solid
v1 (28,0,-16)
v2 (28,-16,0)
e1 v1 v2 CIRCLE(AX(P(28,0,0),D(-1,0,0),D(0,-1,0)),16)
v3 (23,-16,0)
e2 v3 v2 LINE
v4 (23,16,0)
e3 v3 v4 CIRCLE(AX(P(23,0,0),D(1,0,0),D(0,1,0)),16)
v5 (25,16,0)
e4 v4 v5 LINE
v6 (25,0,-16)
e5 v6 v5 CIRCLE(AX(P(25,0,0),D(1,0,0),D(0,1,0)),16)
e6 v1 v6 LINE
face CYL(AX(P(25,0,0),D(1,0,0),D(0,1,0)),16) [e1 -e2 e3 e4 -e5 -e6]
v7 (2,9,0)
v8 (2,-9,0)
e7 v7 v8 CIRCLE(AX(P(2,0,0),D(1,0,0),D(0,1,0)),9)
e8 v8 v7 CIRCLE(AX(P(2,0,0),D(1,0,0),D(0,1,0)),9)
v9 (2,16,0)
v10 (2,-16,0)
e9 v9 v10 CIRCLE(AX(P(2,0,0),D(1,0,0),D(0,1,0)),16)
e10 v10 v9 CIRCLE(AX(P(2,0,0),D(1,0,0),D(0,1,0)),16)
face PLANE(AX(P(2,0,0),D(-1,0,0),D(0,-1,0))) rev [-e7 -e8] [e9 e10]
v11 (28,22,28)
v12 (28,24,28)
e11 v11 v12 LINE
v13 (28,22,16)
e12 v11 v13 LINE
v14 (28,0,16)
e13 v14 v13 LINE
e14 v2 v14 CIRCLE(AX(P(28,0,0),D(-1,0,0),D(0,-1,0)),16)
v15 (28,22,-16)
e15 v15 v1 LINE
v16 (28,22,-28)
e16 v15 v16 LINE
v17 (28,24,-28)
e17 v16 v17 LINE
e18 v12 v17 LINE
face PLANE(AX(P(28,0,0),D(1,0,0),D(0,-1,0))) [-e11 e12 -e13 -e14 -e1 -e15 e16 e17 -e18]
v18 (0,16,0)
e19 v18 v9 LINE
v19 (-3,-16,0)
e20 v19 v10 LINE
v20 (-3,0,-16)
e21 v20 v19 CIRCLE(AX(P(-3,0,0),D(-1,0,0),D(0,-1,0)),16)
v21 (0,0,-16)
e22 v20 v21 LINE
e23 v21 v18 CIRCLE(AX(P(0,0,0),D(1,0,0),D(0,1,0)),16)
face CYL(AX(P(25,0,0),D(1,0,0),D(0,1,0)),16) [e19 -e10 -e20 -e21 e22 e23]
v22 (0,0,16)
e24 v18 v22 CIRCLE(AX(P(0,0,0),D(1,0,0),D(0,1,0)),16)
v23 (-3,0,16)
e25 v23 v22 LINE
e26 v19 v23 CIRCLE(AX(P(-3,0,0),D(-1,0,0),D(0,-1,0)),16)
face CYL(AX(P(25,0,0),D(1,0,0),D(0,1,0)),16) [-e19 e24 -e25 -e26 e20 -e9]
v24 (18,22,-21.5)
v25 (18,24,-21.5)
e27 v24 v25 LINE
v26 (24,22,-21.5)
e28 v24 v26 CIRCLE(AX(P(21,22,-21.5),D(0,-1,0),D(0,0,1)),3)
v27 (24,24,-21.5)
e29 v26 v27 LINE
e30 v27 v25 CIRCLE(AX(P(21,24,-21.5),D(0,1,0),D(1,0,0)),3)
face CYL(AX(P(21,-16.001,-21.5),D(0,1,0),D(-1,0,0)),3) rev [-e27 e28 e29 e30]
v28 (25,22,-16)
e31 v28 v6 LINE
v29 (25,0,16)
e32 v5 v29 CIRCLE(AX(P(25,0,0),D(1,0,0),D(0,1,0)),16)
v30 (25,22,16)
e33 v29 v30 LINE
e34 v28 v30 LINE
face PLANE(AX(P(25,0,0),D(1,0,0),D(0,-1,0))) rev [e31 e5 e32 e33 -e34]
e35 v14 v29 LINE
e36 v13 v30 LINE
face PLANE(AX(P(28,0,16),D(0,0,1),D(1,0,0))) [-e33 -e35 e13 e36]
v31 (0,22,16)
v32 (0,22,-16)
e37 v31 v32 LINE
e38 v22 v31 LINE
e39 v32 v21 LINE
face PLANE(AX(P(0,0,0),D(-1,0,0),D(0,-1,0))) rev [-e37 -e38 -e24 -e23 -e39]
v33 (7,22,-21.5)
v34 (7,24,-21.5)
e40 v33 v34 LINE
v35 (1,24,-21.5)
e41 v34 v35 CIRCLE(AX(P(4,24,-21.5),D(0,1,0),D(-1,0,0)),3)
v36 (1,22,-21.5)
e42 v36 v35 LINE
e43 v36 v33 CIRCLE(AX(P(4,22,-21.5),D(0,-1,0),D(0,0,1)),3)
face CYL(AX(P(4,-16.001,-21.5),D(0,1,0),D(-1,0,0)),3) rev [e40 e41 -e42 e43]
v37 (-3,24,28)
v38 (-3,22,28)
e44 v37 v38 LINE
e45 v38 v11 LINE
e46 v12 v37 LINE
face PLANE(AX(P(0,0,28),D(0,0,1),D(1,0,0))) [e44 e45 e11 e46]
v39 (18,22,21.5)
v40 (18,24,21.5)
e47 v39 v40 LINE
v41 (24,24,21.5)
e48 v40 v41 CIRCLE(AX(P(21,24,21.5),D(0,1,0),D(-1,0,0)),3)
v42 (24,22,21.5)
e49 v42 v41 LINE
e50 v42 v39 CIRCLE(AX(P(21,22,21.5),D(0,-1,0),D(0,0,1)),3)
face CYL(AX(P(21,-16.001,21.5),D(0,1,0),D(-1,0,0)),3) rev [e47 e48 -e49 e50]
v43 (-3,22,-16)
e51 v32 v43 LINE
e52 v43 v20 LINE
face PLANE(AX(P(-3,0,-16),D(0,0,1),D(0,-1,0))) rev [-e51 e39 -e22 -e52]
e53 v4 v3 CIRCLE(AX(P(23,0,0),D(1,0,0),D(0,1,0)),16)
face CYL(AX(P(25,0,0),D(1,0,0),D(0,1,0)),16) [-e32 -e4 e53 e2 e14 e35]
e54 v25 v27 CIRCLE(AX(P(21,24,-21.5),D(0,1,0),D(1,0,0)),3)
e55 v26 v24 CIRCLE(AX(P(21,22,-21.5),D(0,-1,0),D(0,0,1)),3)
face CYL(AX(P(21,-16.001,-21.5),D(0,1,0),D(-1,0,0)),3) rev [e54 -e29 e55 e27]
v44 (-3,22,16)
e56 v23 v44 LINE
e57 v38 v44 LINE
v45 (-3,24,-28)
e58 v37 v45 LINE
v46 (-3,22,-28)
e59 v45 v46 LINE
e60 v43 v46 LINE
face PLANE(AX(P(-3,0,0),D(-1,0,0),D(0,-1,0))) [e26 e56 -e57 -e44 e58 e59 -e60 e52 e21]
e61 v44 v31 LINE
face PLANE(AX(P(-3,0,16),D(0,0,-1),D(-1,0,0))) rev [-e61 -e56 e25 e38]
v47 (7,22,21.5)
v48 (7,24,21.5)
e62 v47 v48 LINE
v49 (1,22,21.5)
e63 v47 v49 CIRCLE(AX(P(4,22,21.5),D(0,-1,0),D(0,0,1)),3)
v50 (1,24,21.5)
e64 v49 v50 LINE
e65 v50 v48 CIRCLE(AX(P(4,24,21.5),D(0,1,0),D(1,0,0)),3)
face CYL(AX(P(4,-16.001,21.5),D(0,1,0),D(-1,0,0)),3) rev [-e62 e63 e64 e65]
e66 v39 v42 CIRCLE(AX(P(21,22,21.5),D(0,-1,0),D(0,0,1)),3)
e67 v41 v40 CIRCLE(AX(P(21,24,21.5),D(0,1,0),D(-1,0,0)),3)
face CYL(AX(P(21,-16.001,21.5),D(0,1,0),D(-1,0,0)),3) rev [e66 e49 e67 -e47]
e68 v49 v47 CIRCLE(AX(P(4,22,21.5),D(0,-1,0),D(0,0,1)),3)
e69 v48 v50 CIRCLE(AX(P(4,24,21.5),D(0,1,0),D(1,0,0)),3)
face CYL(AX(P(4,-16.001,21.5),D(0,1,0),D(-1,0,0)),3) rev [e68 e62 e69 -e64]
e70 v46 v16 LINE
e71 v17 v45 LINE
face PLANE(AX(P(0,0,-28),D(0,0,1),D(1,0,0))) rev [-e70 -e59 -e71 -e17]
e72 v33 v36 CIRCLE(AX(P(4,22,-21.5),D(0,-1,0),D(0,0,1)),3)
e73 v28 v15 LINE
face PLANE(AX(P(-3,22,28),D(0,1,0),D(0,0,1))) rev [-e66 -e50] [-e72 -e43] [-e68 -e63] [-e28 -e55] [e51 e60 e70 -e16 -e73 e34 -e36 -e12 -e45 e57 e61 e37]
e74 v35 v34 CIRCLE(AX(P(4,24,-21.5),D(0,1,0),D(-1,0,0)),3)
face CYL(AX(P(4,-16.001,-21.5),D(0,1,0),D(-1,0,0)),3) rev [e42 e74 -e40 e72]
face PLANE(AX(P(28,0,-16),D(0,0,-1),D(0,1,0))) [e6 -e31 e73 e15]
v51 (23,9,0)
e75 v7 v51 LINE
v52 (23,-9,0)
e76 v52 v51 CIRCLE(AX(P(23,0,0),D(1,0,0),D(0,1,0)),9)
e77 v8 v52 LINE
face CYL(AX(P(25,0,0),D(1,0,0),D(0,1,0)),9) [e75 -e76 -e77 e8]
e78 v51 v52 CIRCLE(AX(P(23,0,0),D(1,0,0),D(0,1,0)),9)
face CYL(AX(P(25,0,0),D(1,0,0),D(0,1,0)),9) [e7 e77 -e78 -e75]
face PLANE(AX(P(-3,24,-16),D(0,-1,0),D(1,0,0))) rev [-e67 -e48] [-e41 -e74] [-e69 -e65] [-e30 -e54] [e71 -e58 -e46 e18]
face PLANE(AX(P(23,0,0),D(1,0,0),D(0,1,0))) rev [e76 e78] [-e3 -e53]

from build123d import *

# Parameters (mm, degrees)
EXTRUDE_START       = 3
EXTRUDE_1_DEPTH     = 3
SKETCH_4_W          = 31
SKETCH_4_H          = 2
EXTRUDE_2_DEPTH     = 28
CUT_EXTRUDE_1_REACH = 58.285
SKETCH_5_R          = 3


with BuildPart() as part:
    # 草图1 → 旋转1 (revolve)
    with BuildSketch(Plane.XY):
        Polygon((2, 16), (0, 16), (0, 0), (25, 0), (25, 16), (23, 16), (23, 9), (2, 9), align=None)
    revolve(axis=Axis((25, 0, 0), (-1, 0, 0)))

    # 草图2 → 凸台-拉伸1 (add)
    with BuildSketch(Plane.ZY.offset(EXTRUDE_START)):
        with BuildLine():
            Line((-16, 0), (-16, 24))
            Line((-16, 24), (16, 24))
            Line((16, 24), (16, 0))
            ThreePointArc((16, 0), (0, -16), (-16, 0))
        make_face()
    extrude_1 = extrude(amount=-EXTRUDE_1_DEPTH)

    # 镜向1: 凸台-拉伸1 across plane
    add(extrude_1.mirror(Plane(origin=(12.5, 0, 0), x_dir=(0, 0, 1), z_dir=(1, 0, 0))))

    # 草图4 → 凸台-拉伸2 (add, symmetric)
    with BuildSketch(Plane.XY):
        with Locations((12.5, 23)):
            Rectangle(SKETCH_4_W, SKETCH_4_H)
    extrude(amount=EXTRUDE_2_DEPTH, both=True)

    # 草图5 → 切除-拉伸1 (cut, up to next)
    with BuildSketch(Plane(origin=(0, 24, 0), x_dir=(1, 0, 0), z_dir=(0, 1, 0)), mode=Mode.PRIVATE) as cut_extrude_1_sk1:
        with Locations(Location((4, 21.5, 0), (0, 0, 180))):
            Circle(SKETCH_5_R)
    cut_extrude_1_tool1 = extrude(cut_extrude_1_sk1.sketch, amount=-CUT_EXTRUDE_1_REACH, mode=Mode.PRIVATE) & part.part
    # 草图5 → 切除-拉伸1 (cut, up to next)
    with BuildSketch(Plane(origin=(0, 24, 0), x_dir=(1, 0, 0), z_dir=(0, 1, 0)), mode=Mode.PRIVATE) as cut_extrude_1_sk2:
        with Locations(Location((4, -21.5, 0), (0, 0, 270))):
            Circle(SKETCH_5_R)
    cut_extrude_1_tool2 = extrude(cut_extrude_1_sk2.sketch, amount=-CUT_EXTRUDE_1_REACH, mode=Mode.PRIVATE) & part.part
    # 草图5 → 切除-拉伸1 (cut, up to next)
    with BuildSketch(Plane(origin=(0, 24, 0), x_dir=(1, 0, 0), z_dir=(0, 1, 0)), mode=Mode.PRIVATE) as cut_extrude_1_sk3:
        with Locations(Location((21, -21.5, 0), (0, 0, 180))):
            Circle(SKETCH_5_R)
    cut_extrude_1_tool3 = extrude(cut_extrude_1_sk3.sketch, amount=-CUT_EXTRUDE_1_REACH, mode=Mode.PRIVATE) & part.part
    # 草图5 → 切除-拉伸1 (cut, up to next)
    with BuildSketch(Plane(origin=(0, 24, 0), x_dir=(1, 0, 0), z_dir=(0, 1, 0)), mode=Mode.PRIVATE) as cut_extrude_1_sk4:
        with Locations(Location((21, 21.5, 0), (0, 0, 270))):
            Circle(SKETCH_5_R)
    cut_extrude_1_tool4 = extrude(cut_extrude_1_sk4.sketch, amount=-CUT_EXTRUDE_1_REACH, mode=Mode.PRIVATE) & part.part
    add(cut_extrude_1_tool1.solids().sort_by_distance((4, 24, -21.5))[0], mode=Mode.SUBTRACT)
    add(cut_extrude_1_tool2.solids().sort_by_distance((4, 24, 21.5))[0], mode=Mode.SUBTRACT)
    add(cut_extrude_1_tool3.solids().sort_by_distance((21, 24, 21.5))[0], mode=Mode.SUBTRACT)
    add(cut_extrude_1_tool4.solids().sort_by_distance((21, 24, -21.5))[0], mode=Mode.SUBTRACT)


solid = part.part
